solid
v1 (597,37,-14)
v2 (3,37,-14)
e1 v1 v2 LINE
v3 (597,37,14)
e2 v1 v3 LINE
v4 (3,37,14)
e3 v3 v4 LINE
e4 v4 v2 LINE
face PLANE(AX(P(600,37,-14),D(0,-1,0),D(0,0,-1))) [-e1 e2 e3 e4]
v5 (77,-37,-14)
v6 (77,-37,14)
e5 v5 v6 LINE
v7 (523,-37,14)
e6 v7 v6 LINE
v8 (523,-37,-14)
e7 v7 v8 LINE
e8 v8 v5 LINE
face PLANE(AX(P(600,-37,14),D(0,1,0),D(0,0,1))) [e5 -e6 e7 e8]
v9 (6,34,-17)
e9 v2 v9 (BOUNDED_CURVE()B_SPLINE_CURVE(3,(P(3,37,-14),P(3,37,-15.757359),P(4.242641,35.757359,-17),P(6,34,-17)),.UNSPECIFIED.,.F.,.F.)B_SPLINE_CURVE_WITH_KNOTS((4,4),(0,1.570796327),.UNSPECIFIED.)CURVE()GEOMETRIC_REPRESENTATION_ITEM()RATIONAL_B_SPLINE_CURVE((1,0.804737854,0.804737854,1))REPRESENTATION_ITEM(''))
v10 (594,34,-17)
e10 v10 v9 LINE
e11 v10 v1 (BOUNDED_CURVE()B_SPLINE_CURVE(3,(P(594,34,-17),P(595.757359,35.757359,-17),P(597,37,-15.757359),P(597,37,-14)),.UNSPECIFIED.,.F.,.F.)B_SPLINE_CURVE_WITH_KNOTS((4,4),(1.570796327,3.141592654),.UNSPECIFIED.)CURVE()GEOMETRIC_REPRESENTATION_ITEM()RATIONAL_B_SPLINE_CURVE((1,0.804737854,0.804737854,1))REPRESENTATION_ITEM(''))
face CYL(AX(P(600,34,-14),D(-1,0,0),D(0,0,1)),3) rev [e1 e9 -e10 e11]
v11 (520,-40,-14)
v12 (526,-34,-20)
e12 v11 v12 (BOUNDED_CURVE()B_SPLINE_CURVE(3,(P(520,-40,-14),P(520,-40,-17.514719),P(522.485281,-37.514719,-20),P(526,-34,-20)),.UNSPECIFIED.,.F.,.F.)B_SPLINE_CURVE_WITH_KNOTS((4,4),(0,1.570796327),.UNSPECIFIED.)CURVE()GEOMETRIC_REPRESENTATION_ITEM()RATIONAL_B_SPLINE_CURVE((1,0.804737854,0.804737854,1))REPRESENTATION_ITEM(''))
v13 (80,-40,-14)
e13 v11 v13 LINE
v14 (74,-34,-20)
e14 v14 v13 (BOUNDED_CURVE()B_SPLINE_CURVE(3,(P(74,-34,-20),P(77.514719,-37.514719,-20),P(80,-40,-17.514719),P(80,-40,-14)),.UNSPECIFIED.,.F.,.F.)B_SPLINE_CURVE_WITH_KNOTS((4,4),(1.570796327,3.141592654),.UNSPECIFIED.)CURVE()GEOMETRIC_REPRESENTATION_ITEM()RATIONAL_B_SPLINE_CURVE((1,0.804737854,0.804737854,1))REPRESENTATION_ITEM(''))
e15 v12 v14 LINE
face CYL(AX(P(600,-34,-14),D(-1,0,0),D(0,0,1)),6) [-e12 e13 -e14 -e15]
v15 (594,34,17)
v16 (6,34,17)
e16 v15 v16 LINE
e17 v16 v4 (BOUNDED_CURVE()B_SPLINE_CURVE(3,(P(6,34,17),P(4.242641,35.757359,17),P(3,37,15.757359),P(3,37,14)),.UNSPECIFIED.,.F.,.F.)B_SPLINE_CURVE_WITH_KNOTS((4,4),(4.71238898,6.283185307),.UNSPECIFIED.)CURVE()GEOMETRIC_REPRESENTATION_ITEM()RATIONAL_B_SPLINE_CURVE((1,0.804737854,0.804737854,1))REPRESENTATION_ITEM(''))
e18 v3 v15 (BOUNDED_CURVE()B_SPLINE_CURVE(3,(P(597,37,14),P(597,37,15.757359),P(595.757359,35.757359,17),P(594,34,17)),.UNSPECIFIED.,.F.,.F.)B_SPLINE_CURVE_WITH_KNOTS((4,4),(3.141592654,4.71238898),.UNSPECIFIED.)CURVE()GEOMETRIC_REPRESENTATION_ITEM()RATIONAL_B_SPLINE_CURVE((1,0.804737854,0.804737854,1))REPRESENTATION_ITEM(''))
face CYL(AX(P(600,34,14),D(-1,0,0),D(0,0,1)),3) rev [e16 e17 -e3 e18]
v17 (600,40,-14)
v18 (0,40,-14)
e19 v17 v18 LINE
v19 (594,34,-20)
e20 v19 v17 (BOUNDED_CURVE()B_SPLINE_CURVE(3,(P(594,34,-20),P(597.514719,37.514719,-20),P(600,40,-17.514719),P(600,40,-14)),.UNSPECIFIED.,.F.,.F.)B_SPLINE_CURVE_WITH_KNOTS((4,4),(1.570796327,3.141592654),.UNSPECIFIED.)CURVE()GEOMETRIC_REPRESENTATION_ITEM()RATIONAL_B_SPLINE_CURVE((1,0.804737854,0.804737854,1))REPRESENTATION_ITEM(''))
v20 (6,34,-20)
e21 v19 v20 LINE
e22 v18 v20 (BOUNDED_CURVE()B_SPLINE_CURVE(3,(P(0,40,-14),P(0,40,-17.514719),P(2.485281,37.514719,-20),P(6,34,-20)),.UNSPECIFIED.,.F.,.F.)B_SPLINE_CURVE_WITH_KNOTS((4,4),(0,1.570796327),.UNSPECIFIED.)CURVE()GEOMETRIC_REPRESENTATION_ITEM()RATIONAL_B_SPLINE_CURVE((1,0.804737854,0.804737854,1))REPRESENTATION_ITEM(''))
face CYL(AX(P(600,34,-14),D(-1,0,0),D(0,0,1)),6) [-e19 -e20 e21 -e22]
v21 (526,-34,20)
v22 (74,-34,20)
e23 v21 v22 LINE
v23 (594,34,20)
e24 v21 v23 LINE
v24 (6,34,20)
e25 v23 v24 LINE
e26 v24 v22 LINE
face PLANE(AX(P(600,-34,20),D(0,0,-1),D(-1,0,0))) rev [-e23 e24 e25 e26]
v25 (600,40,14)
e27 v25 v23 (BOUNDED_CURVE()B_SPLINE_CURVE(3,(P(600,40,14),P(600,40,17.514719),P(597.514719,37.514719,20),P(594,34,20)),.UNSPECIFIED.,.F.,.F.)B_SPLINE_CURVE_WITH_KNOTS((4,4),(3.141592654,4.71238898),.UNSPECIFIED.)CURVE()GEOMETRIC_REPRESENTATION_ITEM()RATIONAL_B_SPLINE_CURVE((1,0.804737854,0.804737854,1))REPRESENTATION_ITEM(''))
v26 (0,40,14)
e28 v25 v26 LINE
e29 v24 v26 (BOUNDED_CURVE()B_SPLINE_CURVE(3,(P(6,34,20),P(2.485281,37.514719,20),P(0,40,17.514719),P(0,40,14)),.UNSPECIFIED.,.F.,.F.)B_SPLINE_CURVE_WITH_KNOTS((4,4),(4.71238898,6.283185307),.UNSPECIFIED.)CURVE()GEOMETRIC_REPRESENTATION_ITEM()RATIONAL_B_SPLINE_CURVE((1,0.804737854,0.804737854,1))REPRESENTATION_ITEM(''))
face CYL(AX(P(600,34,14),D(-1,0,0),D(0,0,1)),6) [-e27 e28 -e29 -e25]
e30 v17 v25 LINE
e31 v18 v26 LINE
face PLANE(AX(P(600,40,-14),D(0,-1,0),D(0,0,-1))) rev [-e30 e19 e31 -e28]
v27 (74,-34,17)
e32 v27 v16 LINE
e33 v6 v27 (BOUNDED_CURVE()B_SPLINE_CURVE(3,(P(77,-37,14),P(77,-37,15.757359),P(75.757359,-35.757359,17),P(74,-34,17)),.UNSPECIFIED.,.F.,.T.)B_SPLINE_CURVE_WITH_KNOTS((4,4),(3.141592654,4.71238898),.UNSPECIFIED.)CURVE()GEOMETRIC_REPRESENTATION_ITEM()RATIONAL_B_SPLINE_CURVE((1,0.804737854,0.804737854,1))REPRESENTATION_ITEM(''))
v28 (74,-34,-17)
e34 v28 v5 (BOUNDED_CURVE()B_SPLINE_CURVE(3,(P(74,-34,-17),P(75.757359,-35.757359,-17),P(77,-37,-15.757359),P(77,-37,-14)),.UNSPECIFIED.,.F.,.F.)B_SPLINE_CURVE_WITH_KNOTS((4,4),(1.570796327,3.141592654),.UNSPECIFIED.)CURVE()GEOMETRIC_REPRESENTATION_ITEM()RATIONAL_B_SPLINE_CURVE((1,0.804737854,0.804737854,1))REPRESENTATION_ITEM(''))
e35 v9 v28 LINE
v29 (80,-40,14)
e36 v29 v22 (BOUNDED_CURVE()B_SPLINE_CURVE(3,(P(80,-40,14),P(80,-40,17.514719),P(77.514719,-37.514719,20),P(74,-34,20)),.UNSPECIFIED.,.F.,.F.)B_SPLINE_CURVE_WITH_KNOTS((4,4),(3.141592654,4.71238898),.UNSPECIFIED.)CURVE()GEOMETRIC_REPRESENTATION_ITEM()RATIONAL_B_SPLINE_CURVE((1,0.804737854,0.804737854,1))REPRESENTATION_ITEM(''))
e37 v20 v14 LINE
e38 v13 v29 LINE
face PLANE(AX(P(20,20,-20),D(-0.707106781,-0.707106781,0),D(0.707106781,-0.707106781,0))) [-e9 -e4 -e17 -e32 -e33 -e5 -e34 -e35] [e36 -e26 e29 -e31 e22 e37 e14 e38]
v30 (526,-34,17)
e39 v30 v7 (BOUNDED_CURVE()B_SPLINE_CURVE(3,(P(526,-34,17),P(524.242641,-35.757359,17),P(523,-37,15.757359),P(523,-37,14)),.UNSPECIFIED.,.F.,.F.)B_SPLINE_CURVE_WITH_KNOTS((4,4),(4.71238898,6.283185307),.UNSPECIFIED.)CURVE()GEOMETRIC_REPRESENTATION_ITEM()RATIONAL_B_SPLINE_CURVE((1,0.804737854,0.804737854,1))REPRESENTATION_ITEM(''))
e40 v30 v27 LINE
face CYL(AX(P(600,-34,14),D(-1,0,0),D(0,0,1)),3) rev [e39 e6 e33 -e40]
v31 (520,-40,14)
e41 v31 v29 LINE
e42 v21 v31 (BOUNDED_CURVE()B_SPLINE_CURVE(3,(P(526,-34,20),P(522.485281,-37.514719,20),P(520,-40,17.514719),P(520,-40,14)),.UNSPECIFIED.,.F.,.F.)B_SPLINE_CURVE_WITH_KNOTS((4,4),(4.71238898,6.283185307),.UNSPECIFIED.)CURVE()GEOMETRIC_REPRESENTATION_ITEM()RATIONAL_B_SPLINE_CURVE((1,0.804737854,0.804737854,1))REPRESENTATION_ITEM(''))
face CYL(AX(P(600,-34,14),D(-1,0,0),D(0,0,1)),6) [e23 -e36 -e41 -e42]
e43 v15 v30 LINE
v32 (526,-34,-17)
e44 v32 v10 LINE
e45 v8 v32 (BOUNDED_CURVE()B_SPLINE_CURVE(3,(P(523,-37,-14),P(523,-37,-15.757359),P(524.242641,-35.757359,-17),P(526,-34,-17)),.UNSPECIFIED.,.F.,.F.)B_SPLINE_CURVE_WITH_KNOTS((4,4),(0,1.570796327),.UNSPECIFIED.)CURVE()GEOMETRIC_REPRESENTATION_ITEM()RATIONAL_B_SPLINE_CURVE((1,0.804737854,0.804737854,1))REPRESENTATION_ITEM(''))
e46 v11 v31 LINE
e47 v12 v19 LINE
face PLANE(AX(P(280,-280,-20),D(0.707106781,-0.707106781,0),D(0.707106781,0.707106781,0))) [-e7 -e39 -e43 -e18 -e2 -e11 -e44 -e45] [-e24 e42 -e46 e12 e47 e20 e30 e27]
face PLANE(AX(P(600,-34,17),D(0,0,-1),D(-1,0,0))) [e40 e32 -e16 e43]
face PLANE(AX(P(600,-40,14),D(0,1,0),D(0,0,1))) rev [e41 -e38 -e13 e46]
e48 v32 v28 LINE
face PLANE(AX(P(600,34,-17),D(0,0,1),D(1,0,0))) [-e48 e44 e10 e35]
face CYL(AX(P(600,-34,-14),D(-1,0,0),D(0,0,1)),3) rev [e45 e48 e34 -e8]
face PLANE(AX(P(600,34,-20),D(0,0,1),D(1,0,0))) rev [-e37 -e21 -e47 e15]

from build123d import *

# Parameters (mm, degrees)
COLD_FORMED_RECT_HOLLOW_SECTION_GB_T_672_DEPTH = 600
CUT_EXTRUDE1_DEPTH                             = 603.660766933


with BuildPart() as part:
    # Sketch1 → Cold-Formed Rect Hollow Section GB/T 6728-2002 80 X 40 X 3(1) (new body)
    with BuildSketch(Plane(origin=(0, 0, 0), x_dir=(0, 0, -1), z_dir=(1, 0, 0))):
        with BuildLine():
            Line((-14, -40), (14, -40))
            ThreePointArc((14, -40), (18.242640687, -38.242640687), (20, -34))
            Line((20, -34), (20, 34))
            ThreePointArc((20, 34), (18.242640687, 38.242640687), (14, 40))
            Line((14, 40), (-14, 40))
            ThreePointArc((-14, 40), (-18.242640687, 38.242640687), (-20, 34))
            Line((-20, 34), (-20, -34))
            ThreePointArc((-20, -34), (-18.242640687, -38.242640687), (-14, -40))
        make_face()
        with BuildLine():
            Line((-14, -37), (14, -37))
            ThreePointArc((14, -37), (16.121320344, -36.121320344), (17, -34))
            Line((17, -34), (17, 34))
            ThreePointArc((17, 34), (16.121320344, 36.121320344), (14, 37))
            Line((14, 37), (-14, 37))
            ThreePointArc((-14, 37), (-16.121320344, 36.121320344), (-17, 34))
            Line((-17, 34), (-17, -34))
            ThreePointArc((-17, -34), (-16.121320344, -36.121320344), (-14, -37))
        make_face(mode=Mode.SUBTRACT)
    extrude(amount=COLD_FORMED_RECT_HOLLOW_SECTION_GB_T_672_DEPTH)

    # Sketch2 → Cut-Extrude1 (cut, through all)
    with BuildSketch(Plane.XY.offset(20)):
        Polygon((74, -34), (6, 34), (0, 34), (0, -34), align=None)
        Polygon((600, 34), (594, 34), (526, -34), (600, -34), align=None)
        Polygon((600, -34), (526, -34), (520, -40), (600, -40), align=None)
        Polygon((6, 34), (0, 40), (0, 34), align=None)
        Polygon((600, 40), (594, 34), (600, 34), align=None)
        Polygon((80, -40), (74, -34), (0, -34), (0, -40), align=None)
    extrude(amount=-CUT_EXTRUDE1_DEPTH, mode=Mode.SUBTRACT)


solid = part.part
